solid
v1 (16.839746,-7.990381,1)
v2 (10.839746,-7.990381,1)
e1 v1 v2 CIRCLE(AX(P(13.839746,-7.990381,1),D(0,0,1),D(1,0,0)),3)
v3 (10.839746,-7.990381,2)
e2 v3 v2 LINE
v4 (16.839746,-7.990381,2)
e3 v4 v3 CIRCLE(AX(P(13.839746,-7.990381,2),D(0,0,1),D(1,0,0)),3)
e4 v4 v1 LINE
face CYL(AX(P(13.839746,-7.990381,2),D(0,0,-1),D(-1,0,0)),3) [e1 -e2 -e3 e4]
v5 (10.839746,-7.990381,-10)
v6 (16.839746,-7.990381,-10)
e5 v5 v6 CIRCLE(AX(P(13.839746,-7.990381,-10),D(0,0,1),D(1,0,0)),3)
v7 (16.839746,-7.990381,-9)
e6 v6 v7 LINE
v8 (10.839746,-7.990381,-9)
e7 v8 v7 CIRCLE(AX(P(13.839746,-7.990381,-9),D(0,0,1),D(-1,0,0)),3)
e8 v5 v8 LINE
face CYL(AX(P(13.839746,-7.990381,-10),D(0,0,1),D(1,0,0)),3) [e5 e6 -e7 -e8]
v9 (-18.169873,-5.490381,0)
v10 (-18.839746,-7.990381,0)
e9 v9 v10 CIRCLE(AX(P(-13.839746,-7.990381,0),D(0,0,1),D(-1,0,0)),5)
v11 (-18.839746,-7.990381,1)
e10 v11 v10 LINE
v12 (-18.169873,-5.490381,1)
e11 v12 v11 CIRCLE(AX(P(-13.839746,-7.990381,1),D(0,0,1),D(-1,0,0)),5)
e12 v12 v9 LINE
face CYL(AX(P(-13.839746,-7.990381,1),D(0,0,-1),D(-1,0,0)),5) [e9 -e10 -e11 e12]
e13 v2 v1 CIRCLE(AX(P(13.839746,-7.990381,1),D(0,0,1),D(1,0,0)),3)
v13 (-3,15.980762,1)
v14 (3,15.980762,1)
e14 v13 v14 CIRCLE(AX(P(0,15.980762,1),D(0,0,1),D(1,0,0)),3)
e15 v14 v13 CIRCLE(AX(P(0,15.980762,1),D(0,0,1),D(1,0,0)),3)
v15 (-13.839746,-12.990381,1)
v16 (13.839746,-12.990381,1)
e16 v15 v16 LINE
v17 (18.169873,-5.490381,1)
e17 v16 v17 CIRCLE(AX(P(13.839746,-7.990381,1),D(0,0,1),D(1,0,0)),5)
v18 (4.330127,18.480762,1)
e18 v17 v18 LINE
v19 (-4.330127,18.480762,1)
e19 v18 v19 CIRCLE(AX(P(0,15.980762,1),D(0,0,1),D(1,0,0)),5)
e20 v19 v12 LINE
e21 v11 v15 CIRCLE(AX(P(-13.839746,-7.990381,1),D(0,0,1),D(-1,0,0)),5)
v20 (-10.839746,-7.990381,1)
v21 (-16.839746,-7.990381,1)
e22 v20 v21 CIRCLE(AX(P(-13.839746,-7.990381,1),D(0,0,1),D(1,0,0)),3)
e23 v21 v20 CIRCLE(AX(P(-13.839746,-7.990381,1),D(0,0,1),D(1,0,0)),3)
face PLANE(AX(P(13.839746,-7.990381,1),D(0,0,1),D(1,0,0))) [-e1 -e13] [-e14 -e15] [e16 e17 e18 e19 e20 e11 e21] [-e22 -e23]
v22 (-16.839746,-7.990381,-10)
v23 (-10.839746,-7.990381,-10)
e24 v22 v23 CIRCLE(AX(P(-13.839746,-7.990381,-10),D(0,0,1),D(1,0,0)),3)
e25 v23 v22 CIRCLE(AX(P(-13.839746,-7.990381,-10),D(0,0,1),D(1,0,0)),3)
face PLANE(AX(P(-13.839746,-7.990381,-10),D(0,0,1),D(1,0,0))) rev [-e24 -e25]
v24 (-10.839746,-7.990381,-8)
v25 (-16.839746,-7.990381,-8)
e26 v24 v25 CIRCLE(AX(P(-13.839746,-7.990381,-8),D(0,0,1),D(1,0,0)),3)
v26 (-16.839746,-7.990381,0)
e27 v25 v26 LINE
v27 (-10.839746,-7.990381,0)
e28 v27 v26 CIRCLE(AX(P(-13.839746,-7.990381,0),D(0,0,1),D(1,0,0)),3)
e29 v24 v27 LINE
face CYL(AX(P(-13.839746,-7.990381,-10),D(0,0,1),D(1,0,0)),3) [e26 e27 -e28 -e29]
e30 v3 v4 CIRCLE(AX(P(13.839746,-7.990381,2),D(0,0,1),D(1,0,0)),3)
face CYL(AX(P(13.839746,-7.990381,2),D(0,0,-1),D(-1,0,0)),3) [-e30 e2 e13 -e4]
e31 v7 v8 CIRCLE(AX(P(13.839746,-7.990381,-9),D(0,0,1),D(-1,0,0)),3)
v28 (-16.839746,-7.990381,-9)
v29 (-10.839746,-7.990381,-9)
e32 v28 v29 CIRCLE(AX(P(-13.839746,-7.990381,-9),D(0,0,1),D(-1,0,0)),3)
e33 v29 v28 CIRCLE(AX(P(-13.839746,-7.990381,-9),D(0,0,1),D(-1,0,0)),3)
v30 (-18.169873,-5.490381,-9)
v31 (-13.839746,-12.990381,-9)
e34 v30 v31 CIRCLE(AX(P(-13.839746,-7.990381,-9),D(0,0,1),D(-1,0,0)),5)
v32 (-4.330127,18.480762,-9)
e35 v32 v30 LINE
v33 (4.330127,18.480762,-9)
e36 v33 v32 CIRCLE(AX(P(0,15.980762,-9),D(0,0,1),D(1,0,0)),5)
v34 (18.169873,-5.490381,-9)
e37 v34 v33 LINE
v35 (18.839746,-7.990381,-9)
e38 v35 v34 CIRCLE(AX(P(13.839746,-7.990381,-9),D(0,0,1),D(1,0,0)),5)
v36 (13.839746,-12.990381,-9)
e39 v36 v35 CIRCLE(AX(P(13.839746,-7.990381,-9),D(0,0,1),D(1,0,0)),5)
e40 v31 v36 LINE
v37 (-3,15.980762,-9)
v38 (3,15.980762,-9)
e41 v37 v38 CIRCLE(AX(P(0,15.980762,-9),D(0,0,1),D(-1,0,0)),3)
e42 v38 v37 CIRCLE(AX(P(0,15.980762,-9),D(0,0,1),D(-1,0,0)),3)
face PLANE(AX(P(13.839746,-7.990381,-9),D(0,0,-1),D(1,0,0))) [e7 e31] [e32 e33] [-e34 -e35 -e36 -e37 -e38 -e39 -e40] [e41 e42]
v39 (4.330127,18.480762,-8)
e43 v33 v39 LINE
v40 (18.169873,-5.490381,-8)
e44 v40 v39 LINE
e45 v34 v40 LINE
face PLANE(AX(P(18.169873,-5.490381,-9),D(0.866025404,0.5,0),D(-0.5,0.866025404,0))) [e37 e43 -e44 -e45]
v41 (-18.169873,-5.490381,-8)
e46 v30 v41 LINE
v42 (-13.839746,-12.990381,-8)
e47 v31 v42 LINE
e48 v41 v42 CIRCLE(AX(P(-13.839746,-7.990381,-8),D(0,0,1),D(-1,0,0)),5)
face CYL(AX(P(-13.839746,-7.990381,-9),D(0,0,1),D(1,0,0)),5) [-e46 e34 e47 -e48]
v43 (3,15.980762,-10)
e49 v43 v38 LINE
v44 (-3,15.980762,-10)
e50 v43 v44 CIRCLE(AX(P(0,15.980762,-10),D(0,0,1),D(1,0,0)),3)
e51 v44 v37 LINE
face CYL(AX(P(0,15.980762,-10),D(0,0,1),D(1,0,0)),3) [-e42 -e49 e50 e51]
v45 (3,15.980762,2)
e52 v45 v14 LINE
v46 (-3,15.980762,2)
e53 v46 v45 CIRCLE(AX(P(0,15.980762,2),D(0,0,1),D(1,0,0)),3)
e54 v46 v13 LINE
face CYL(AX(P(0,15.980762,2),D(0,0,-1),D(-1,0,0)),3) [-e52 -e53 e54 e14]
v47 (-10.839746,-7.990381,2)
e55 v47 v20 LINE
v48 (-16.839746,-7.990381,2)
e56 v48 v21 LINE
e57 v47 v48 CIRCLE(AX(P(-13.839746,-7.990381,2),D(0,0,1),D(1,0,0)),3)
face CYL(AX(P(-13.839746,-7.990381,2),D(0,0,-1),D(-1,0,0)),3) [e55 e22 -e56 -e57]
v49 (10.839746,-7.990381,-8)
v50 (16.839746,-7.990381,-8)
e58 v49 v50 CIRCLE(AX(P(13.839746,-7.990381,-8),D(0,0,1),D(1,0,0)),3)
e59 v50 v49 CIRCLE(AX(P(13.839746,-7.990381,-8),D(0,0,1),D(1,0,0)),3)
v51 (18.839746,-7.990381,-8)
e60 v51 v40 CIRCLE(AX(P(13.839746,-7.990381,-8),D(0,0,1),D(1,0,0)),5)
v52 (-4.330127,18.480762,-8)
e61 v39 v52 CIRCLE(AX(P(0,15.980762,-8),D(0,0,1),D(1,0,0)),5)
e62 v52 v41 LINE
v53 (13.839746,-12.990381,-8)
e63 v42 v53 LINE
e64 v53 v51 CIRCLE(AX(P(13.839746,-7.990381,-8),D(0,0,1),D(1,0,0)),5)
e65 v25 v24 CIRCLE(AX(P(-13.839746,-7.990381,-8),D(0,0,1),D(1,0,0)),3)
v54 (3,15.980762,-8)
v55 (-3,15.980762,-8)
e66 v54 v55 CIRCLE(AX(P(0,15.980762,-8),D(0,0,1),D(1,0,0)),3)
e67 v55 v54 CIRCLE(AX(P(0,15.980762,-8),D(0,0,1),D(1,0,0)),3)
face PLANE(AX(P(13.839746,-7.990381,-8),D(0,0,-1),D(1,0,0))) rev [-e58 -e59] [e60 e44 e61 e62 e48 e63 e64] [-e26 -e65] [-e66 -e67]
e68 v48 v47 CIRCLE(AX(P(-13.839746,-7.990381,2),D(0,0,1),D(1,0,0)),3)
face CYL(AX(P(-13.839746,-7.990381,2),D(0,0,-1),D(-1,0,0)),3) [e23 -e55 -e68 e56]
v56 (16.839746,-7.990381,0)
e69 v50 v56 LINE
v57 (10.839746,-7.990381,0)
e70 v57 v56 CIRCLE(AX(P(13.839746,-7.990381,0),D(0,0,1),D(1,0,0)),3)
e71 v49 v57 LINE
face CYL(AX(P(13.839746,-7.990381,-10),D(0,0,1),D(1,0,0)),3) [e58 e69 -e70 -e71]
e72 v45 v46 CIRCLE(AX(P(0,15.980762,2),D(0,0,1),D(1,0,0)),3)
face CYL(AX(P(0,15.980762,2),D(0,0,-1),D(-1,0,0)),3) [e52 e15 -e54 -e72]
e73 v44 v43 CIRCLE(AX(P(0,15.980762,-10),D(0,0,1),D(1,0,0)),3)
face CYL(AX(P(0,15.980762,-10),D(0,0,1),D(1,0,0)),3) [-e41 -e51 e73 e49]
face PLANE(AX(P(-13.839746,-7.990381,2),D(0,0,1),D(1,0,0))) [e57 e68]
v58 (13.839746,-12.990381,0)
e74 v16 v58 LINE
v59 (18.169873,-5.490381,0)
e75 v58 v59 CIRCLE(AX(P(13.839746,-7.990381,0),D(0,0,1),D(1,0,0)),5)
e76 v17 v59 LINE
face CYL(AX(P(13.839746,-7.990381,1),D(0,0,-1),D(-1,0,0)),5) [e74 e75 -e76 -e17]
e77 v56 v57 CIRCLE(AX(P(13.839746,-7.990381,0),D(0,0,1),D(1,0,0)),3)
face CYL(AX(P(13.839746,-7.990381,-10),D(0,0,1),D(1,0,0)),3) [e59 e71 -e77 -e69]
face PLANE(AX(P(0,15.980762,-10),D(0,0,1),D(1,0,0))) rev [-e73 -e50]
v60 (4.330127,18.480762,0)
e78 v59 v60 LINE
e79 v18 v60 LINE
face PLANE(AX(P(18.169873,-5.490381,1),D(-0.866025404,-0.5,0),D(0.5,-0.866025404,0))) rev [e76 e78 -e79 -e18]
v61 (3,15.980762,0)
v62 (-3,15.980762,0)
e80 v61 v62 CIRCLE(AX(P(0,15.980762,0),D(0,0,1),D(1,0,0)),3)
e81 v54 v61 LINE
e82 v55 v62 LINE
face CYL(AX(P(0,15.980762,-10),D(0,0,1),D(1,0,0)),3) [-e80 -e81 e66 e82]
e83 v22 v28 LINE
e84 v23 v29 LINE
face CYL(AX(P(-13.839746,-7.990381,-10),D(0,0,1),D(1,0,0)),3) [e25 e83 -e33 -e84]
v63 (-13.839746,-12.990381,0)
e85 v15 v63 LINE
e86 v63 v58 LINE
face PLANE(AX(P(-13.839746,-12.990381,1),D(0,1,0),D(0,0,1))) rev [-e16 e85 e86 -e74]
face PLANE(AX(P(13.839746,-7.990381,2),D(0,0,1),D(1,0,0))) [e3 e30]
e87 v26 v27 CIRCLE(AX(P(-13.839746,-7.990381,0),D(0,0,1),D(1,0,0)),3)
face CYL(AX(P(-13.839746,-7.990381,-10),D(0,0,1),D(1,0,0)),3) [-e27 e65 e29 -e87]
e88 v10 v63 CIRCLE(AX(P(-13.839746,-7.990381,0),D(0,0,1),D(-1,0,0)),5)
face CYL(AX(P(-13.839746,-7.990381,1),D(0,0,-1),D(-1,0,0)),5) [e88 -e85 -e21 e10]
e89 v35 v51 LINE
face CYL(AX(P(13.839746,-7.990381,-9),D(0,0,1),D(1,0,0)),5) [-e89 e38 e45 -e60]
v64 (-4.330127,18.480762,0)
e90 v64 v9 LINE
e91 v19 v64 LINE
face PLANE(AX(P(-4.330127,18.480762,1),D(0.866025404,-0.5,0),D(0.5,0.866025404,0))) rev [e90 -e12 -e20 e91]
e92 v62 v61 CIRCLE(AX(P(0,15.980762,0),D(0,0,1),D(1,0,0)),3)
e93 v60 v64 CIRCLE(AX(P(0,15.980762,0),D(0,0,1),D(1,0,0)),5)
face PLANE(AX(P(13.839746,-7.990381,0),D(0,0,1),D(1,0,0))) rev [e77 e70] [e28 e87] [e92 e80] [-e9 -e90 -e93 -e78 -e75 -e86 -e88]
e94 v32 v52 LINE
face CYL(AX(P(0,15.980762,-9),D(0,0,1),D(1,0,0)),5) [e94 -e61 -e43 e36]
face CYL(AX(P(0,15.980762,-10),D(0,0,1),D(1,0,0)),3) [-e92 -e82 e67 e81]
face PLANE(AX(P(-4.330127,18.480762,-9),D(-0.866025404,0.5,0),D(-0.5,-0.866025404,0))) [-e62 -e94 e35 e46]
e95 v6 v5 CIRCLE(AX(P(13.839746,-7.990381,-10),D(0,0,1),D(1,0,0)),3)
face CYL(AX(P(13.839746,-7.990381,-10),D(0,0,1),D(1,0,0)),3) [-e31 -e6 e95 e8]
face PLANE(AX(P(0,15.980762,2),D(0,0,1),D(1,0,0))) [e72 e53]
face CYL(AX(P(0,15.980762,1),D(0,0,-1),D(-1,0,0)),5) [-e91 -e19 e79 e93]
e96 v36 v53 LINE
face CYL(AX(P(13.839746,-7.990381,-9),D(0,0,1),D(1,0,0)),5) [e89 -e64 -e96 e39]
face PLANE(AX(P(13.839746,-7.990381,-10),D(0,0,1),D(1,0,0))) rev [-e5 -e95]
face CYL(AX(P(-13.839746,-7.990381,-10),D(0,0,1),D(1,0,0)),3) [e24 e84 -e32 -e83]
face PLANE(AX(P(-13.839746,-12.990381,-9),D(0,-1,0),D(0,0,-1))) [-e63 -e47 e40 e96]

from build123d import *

# Parameters (mm, degrees)
SKETCH1_R           = 3
BOSS_EXTRUDE1_DEPTH = 1
BOSS_EXTRUDE2_START = -11
SKETCH2_R           = 3
BOSS_EXTRUDE2_DEPTH = 11
SKETCH3_R           = 3
BOSS_EXTRUDE3_DEPTH = 1


with BuildPart() as part:
    # Sketch1 → Boss-Extrude1 (new body)
    with BuildSketch(Plane.XY):
        with BuildLine():
            Line((18.169872981, -5.490381057), (4.330127019, 18.480762114))
            ThreePointArc((4.330127019, 18.480762114), (0, 20.980762114), (-4.330127019, 18.480762114))
            Line((-4.330127019, 18.480762114), (-18.169872981, -5.490381057))
            ThreePointArc((-18.169872981, -5.490381057), (-18.169872981, -10.490381057), (-13.839745962, -12.990381057))
            Line((-13.839745962, -12.990381057), (13.839745962, -12.990381057))
            ThreePointArc((13.839745962, -12.990381057), (18.169872981, -10.490381057), (18.169872981, -5.490381057))
        make_face()
        with Locations((0, 15.980762114)):
            Circle(SKETCH1_R, mode=Mode.SUBTRACT)
        with Locations((13.839745962, -7.990381057)):
            Circle(SKETCH1_R, mode=Mode.SUBTRACT)
        with Locations((-13.839745962, -7.990381057)):
            Circle(SKETCH1_R, mode=Mode.SUBTRACT)
    boss_extrude1 = extrude(amount=BOSS_EXTRUDE1_DEPTH)

    # Sketch2 → Boss-Extrude2 (add)
    with BuildSketch(Plane.XY.offset(1).offset(BOSS_EXTRUDE2_START)):
        with Locations((13.839745962, -7.990381057)):
            Circle(SKETCH2_R)
        with Locations((-13.839745962, -7.990381057)):
            Circle(SKETCH2_R)
        with Locations((0, 15.980762114)):
            Circle(SKETCH2_R)
    extrude(amount=BOSS_EXTRUDE2_DEPTH)

    # Mirror3: Boss-Extrude1 across plane
    add(boss_extrude1.mirror(Plane(origin=(0, 0, -4), x_dir=(1, 0, 0), z_dir=(0, 0, -1))))

    # Sketch3 → Boss-Extrude3 (add)
    with BuildSketch(Plane.XY.offset(1)):
        with Locations((0, 15.980762114)):
            Circle(SKETCH3_R)
        with Locations((13.839745962, -7.990381057)):
            Circle(SKETCH3_R)
        with Locations((-13.839745962, -7.990381057)):
            Circle(SKETCH3_R)
    extrude(amount=BOSS_EXTRUDE3_DEPTH)


solid = part.part
